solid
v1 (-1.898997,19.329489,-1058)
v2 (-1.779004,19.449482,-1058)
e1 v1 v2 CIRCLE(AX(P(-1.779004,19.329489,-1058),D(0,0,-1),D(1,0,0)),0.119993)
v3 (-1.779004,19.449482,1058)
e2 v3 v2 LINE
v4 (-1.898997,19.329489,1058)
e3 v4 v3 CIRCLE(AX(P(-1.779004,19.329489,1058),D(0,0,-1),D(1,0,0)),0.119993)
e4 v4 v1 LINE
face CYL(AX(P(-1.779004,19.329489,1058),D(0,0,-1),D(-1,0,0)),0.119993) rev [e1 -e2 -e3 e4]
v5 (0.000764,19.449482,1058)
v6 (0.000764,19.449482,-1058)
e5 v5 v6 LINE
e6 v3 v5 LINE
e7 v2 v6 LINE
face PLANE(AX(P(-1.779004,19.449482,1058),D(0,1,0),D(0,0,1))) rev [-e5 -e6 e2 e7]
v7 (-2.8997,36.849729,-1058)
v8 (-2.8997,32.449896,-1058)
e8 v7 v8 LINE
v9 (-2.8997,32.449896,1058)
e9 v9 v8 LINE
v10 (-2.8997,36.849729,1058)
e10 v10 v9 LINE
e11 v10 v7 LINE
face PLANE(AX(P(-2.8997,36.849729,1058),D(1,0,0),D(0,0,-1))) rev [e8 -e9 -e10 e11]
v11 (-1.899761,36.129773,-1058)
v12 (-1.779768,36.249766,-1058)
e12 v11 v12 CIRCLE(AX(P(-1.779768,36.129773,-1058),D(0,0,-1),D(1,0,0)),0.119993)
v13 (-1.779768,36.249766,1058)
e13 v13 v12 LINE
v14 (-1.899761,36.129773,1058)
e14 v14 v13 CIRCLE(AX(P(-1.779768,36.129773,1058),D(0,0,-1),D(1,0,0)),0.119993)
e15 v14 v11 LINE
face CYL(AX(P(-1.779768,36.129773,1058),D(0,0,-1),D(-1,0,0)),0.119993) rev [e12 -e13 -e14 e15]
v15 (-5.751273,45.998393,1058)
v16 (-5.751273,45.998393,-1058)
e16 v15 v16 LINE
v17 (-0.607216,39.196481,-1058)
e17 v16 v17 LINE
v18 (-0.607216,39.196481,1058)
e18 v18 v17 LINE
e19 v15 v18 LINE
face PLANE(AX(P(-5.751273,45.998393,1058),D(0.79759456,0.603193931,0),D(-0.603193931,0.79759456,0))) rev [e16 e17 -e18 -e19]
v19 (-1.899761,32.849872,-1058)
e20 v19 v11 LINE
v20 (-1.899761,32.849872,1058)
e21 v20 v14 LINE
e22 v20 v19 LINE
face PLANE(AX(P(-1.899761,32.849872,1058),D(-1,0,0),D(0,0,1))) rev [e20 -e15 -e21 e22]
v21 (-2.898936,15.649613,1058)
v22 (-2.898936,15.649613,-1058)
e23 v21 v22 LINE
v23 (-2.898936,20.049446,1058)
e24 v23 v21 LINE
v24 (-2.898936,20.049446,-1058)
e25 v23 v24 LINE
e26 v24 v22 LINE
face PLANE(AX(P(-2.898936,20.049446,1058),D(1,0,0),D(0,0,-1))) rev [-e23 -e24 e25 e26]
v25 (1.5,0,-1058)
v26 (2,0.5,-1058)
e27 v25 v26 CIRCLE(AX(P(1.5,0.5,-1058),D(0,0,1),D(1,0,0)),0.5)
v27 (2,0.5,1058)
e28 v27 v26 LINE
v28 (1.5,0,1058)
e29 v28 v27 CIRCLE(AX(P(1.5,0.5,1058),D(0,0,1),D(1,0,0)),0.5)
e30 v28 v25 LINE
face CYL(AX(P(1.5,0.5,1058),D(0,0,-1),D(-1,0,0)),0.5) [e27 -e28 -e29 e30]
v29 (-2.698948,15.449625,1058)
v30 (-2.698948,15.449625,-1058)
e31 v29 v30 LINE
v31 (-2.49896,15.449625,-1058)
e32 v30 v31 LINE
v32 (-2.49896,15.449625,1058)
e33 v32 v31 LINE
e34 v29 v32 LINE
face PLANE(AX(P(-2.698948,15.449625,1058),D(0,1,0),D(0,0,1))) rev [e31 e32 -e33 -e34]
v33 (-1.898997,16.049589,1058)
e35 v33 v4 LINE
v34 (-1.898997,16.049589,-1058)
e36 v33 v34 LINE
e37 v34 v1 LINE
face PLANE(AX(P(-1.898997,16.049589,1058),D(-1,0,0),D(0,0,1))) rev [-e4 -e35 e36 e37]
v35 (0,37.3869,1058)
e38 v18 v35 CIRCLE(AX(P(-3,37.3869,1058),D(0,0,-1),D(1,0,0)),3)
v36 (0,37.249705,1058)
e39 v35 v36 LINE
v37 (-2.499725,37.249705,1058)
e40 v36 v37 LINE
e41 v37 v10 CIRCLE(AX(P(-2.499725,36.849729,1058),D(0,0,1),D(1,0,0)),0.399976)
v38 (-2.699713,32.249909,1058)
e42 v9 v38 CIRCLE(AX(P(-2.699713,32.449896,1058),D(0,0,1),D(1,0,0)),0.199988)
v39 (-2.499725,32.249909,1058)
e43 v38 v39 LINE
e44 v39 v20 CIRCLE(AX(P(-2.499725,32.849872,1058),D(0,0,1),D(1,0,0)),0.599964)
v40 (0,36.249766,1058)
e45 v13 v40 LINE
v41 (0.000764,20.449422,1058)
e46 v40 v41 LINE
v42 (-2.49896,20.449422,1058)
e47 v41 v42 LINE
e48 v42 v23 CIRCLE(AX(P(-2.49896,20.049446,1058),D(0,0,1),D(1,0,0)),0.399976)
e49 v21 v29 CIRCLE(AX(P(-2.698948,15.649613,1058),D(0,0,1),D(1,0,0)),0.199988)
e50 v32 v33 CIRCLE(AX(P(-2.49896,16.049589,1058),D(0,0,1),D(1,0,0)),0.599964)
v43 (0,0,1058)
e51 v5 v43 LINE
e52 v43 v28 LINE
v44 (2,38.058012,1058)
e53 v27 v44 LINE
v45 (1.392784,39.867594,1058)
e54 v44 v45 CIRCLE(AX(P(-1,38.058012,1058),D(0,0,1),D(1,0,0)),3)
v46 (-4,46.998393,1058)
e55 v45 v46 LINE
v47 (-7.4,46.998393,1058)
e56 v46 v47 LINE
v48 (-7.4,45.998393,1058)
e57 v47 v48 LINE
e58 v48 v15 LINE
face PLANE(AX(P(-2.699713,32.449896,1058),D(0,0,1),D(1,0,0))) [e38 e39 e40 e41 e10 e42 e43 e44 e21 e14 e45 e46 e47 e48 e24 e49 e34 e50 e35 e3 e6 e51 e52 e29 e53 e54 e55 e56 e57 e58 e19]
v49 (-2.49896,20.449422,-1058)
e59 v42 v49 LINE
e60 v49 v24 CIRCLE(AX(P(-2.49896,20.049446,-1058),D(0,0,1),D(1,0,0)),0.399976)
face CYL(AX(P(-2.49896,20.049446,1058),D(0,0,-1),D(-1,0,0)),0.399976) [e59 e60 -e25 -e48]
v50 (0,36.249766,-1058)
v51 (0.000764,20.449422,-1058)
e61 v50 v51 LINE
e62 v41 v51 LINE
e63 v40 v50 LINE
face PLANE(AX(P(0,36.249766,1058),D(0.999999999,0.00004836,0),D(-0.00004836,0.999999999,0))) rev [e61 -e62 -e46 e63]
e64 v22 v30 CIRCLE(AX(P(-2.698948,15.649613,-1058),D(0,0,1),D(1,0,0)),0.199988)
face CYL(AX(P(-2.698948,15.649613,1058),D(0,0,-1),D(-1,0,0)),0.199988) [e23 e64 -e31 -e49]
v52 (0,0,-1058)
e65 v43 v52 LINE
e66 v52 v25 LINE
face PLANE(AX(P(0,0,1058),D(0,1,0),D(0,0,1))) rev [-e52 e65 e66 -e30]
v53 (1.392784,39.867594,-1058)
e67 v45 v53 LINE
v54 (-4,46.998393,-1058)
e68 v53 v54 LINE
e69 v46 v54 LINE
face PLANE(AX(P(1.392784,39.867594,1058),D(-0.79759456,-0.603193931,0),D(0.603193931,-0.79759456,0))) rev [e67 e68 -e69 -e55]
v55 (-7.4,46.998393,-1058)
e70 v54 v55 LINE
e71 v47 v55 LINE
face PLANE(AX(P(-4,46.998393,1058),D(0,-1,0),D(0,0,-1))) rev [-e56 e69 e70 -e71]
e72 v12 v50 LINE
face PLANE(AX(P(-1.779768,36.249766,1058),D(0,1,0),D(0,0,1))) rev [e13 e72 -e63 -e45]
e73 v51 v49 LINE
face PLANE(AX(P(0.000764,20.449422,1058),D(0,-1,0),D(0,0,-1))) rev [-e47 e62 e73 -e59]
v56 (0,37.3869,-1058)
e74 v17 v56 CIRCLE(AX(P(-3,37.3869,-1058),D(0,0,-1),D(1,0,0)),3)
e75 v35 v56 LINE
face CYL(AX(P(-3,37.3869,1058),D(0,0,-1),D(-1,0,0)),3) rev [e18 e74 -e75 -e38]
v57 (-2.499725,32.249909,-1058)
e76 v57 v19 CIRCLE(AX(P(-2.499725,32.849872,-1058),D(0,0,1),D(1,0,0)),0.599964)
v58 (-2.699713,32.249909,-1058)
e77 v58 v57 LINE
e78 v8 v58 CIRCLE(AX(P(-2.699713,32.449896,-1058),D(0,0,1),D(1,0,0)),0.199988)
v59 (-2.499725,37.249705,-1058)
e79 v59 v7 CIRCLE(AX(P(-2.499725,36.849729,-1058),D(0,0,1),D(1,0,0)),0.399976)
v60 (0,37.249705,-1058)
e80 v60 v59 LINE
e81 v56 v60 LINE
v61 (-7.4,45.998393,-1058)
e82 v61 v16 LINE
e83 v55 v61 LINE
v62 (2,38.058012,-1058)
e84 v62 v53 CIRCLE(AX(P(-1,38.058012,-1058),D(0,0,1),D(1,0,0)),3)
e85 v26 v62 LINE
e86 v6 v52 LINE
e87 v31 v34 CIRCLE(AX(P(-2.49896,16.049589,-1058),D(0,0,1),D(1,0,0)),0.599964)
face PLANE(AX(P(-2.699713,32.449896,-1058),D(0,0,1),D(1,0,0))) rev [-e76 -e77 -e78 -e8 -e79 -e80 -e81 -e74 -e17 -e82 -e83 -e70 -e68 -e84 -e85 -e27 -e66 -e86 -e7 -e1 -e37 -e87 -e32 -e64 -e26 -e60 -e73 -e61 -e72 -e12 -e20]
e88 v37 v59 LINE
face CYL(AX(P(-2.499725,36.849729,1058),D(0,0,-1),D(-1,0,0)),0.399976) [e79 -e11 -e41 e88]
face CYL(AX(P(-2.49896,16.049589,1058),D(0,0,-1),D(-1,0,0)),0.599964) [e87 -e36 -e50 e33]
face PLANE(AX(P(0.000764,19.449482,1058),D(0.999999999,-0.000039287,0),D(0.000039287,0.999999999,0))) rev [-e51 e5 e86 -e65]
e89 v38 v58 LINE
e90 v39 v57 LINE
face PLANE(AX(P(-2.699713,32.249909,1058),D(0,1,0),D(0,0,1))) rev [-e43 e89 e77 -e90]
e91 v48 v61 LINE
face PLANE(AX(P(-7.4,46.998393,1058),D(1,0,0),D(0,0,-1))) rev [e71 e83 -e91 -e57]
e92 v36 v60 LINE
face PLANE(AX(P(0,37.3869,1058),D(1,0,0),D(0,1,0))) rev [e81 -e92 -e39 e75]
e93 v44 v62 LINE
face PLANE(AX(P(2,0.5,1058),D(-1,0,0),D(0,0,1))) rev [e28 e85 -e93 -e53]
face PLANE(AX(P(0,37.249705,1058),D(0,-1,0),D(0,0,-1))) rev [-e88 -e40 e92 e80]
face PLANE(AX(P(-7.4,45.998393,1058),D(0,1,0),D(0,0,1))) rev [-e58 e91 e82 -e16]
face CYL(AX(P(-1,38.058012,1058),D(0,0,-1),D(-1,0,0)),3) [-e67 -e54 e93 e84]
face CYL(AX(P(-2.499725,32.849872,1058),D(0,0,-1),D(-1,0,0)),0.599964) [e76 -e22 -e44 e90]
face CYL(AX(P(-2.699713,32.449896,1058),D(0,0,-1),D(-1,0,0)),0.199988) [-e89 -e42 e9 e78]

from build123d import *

# Parameters (mm, degrees)
EXTRUDE_1_DEPTH = 1058


with BuildPart() as part:
    # 草图2 → 凸台-拉伸1 (new, symmetric)
    with BuildSketch(Plane.XY):
        with BuildLine():
            Line((-2.699712502, 32.249908534), (-2.499724552, 32.249908534))
            ThreePointArc((-2.499724552, 32.249908534), (-2.075486045, 32.425633877), (-1.899760702, 32.849872384))
            Line((-1.899760702, 32.849872384), (-1.899760702, 36.12977276))
            ThreePointArc((-1.899760702, 36.12977276), (-1.864615633, 36.214620461), (-1.779767932, 36.24976553))
            Line((-1.779767932, 36.24976553), (0, 36.24976553))
            Line((0, 36.24976553), (0.000764104, 20.44942184))
            Line((0.000764104, 20.44942184), (-2.498960448, 20.44942184))
            ThreePointArc((-2.498960448, 20.44942184), (-2.781786119, 20.332271611), (-2.898936348, 20.04944594))
            Line((-2.898936348, 20.04944594), (-2.898936348, 15.649613044))
            ThreePointArc((-2.898936348, 15.649613044), (-2.840361233, 15.508200208), (-2.698948398, 15.449625094))
            Line((-2.698948398, 15.449625094), (-2.498960448, 15.449625094))
            ThreePointArc((-2.498960448, 15.449625094), (-2.074721941, 15.625350437), (-1.898996598, 16.049588944))
            Line((-1.898996598, 16.049588944), (-1.898996598, 19.32948932))
            ThreePointArc((-1.898996598, 19.32948932), (-1.863851529, 19.414337021), (-1.779003828, 19.44948209))
            Line((-1.779003828, 19.44948209), (0.000764104, 19.44948209))
            Line((0.000764104, 19.44948209), (0, 0))
            Line((0, 0), (1.5, 0))
            ThreePointArc((1.5, 0), (1.853553391, 0.146446609), (2, 0.5))
            Line((2, 0.5), (2, 38.058011928))
            ThreePointArc((2, 38.058011928), (1.844147591, 39.012383177), (1.392783679, 39.867593721))
            Line((1.392783679, 39.867593721), (-4, 46.998393128))
            Line((-4, 46.998393128), (-7.4, 46.998393128))
            Line((-7.4, 46.998393128), (-7.4, 45.998393128))
            Line((-7.4, 45.998393128), (-5.751273316, 45.998393128))
            Line((-5.751273316, 45.998393128), (-0.607216321, 39.196481397))
            ThreePointArc((-0.607216321, 39.196481397), (-0.155852409, 38.341270854), (0, 37.386899605))
            Line((0, 37.386899605), (0, 37.24970528))
            Line((0, 37.24970528), (-2.499724552, 37.24970528))
            ThreePointArc((-2.499724552, 37.24970528), (-2.782550223, 37.132555051), (-2.899700452, 36.84972938))
            Line((-2.899700452, 36.84972938), (-2.899700452, 32.449896484))
            ThreePointArc((-2.899700452, 32.449896484), (-2.841125337, 32.308483648), (-2.699712502, 32.249908534))
        make_face()
    extrude(amount=EXTRUDE_1_DEPTH, both=True)


solid = part.part
